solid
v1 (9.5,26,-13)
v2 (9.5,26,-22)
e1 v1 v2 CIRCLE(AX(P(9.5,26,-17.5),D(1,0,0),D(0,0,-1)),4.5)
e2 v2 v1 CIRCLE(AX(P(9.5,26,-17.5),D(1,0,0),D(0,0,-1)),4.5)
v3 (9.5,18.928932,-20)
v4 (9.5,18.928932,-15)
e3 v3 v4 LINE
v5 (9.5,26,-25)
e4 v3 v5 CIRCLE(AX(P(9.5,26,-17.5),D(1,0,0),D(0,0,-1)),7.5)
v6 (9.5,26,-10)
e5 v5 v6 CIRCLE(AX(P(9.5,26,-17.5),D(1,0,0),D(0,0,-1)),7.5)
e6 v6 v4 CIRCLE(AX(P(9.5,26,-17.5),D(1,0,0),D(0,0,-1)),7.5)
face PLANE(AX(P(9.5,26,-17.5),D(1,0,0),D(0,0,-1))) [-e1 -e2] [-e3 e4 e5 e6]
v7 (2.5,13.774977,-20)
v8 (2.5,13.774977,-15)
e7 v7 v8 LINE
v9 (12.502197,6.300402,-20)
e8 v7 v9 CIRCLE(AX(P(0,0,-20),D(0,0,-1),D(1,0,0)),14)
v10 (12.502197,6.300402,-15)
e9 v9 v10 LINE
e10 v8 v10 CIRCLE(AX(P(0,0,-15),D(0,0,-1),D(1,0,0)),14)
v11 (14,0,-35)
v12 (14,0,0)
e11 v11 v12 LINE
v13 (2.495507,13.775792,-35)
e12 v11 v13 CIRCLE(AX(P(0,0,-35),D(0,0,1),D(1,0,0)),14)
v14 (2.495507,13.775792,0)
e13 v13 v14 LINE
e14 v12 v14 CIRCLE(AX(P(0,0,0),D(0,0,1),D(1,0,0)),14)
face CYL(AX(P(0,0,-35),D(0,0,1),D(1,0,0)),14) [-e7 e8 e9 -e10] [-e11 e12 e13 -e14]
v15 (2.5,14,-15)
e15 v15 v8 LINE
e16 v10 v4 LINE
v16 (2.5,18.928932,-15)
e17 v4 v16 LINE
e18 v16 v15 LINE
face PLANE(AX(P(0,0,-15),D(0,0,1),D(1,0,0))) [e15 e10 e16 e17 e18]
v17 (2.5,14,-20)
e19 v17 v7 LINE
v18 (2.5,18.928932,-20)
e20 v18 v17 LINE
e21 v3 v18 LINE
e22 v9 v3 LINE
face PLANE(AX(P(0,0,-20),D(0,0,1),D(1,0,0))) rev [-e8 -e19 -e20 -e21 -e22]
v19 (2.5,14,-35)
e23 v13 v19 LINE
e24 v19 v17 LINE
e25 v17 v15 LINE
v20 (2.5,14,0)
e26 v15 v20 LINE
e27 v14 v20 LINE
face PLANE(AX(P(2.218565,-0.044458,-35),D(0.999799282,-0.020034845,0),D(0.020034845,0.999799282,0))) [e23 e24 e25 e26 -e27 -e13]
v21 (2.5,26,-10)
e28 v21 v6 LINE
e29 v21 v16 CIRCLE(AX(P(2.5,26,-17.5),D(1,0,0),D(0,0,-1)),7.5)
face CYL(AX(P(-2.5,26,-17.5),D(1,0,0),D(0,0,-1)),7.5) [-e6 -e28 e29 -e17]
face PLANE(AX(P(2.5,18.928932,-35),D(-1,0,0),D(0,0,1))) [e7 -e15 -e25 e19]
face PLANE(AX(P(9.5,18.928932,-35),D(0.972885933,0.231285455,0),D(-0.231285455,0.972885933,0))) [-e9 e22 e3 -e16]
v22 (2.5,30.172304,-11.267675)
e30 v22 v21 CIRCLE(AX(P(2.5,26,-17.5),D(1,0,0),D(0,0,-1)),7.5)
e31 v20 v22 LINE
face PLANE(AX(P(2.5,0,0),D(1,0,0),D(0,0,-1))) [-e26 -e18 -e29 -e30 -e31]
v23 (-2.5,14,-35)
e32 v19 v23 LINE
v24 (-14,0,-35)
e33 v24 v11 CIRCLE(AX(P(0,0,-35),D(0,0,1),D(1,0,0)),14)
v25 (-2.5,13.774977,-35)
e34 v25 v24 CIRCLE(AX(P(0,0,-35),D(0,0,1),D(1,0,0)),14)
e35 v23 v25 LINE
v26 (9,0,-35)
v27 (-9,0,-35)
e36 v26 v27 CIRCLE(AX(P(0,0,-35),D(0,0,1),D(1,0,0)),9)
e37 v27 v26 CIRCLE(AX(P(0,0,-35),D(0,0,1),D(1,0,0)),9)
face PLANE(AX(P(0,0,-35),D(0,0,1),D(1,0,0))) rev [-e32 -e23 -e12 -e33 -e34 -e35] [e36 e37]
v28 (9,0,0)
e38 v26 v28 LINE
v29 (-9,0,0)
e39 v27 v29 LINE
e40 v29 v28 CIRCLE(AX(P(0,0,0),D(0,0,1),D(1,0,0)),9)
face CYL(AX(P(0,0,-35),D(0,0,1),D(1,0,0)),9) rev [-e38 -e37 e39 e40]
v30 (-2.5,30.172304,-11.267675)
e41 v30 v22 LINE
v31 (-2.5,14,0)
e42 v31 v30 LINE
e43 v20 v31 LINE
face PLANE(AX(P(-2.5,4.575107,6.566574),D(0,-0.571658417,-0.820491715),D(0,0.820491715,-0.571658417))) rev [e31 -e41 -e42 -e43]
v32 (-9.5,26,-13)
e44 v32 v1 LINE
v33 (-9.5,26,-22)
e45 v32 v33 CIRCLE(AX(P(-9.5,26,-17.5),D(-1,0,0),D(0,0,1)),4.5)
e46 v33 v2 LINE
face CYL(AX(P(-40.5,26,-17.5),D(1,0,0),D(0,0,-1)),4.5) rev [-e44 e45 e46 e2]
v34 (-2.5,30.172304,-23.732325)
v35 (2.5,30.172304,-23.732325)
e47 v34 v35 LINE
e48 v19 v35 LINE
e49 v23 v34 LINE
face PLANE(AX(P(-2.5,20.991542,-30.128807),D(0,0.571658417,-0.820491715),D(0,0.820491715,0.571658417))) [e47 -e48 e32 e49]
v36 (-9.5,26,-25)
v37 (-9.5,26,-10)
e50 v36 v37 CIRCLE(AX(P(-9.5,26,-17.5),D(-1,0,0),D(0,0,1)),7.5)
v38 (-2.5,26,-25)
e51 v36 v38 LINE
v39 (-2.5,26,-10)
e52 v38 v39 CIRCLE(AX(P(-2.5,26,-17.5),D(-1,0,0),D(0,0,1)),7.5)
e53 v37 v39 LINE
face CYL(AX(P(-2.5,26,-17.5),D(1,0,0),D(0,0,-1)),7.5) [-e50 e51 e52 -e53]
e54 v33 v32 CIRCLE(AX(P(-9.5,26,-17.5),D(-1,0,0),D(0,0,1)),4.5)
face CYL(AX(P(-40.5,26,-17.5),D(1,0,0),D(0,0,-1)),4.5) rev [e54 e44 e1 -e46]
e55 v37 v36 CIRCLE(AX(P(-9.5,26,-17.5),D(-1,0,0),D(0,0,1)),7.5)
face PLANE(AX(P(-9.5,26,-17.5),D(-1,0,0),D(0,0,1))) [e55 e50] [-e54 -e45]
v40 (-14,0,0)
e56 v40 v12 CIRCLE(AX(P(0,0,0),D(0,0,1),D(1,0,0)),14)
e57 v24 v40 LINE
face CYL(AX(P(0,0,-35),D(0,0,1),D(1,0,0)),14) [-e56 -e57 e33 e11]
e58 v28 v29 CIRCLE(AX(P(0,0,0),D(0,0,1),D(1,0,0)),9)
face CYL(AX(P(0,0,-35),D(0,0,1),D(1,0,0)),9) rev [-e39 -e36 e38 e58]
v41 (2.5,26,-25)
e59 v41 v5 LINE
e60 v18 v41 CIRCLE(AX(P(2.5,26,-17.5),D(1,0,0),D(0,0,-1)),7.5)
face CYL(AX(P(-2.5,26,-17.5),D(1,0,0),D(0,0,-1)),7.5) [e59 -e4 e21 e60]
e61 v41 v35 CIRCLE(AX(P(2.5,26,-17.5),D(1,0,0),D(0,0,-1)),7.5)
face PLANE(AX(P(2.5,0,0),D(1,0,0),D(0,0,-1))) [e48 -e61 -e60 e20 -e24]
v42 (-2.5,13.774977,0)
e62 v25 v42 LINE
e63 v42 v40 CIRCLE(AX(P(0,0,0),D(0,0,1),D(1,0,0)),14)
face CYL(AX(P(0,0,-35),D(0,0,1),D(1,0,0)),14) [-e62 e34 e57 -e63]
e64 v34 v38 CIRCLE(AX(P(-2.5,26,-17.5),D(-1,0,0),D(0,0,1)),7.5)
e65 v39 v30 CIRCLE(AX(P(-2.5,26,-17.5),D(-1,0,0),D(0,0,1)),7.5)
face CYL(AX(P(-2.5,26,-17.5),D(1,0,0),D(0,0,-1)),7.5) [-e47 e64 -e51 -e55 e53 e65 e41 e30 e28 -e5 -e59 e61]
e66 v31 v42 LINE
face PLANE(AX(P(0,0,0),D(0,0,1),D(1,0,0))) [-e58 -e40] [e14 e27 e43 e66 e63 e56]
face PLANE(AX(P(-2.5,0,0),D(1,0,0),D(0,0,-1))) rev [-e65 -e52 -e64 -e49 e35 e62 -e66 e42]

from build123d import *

# Parameters (mm, degrees)
MAIN_CYLINDER_SKETCH_R = 14
MAIN_CYLINDER_28_DEPTH = 35
MAIN_BORE_SKETCH_R     = 9
MAIN_BORE_18_DEPTH     = 35
BASE_WEB_SKETCH_R      = 7.5
BASE_WEB_DEPTH         = 2.5
SECOND_WEB_DEPTH       = 2.5
SUPPORT_RIB_DEPTH      = 5
UPPER_BOSS_A_SKETCH_R  = 7.5
UPPER_BOSS_A_15_DEPTH  = 7
UPPER_BOSS_B_SKETCH_R  = 7.5
UPPER_BOSS_B_15_DEPTH  = 7
BOSS_ARM_DEPTH         = 7
SADDLE_FILL_DEPTH      = 35
TRIM_CUT_1_DEPTH       = 15
TRIM_CUT_2_DEPTH       = 51.430645445
TRIM_CUT_2_DEPTH_BACK  = 15
TRIM_CUT_3_DEPTH       = 15
UPPER_BORE_SKETCH_R    = 4.5
UPPER_BORE_9_DEPTH     = 50
CYLINDER_SKIN_28_DEPTH = 35


with BuildPart() as part:
    # Main Cylinder Sketch → Main Cylinder Ø28 (new body)
    with BuildSketch(Plane.XY):
        Circle(MAIN_CYLINDER_SKETCH_R)
    extrude(amount=-MAIN_CYLINDER_28_DEPTH)

    # Main Bore Sketch → Main Bore Ø18 (cut)
    with BuildSketch(Plane.XY):
        Circle(MAIN_BORE_SKETCH_R)
    extrude(amount=-MAIN_BORE_18_DEPTH, mode=Mode.SUBTRACT)



with BuildPart() as body_2:
    # Base Web Sketch → Base Web (new body)
    with BuildSketch(Plane(origin=(0, 0, 0), x_dir=(0, 0, -1), z_dir=(1, 0, 0))):
        with Locations((17.5, 26)):
            Circle(BASE_WEB_SKETCH_R)
        with BuildLine():
            Line((35, 14), (25, 26))
            ThreePointArc((25, 26), (17.5, 18.5), (10, 26))
            Line((10, 26), (0, 14))
            Line((0, 14), (35, 14))
        make_face()
    extrude(amount=-BASE_WEB_DEPTH)

    # Second Web Sketch → Second Web (add)
    with BuildSketch(Plane(origin=(0, 0, 0), x_dir=(0, 0, -1), z_dir=(1, 0, 0))):
        with BuildLine():
            ThreePointArc((25, 26), (17.5, 33.5), (10, 26))
            ThreePointArc((10, 26), (17.5, 18.5), (25, 26))
        make_face()
        with BuildLine():
            Line((10, 26), (0, 14))
            Line((0, 14), (35, 14))
            Line((35, 14), (25, 26))
            ThreePointArc((25, 26), (17.5, 18.5), (10, 26))
        make_face()
    extrude(amount=SECOND_WEB_DEPTH)

    # Support Rib Sketch → Support Rib (add)
    with BuildSketch(Plane(origin=(2.5, 0, 0), x_dir=(0, 0, -1), z_dir=(1, 0, 0))):
        with BuildLine():
            Line((11.267674623, 30.172303968), (0, 14))
            Line((0, 14), (10, 26))
            ThreePointArc((10, 26), (10.323913311, 28.180316454), (11.267674623, 30.172303968))
        make_face()
        with BuildLine():
            Line((25, 26), (35, 14))
            Line((35, 14), (23.732325377, 30.172303968))
            ThreePointArc((23.732325377, 30.172303968), (24.676086689, 28.180316454), (25, 26))
        make_face()
    extrude(amount=-SUPPORT_RIB_DEPTH)

    # Upper Boss A Sketch → Upper Boss A Ø15 (add)
    with BuildSketch(Plane(origin=(2.5, 0, 0), x_dir=(0, 0, -1), z_dir=(1, 0, 0))):
        with Locations((17.5, 26)):
            Circle(UPPER_BOSS_A_SKETCH_R)
    extrude(amount=UPPER_BOSS_A_15_DEPTH)

    # Upper Boss B Sketch → Upper Boss B Ø15 (add)
    with BuildSketch(Plane.ZY.offset(2.5)):
        with Locations(Location((-17.5, 26, 0), (0, 0, 180))):
            Circle(UPPER_BOSS_B_SKETCH_R)
    extrude(amount=UPPER_BOSS_B_15_DEPTH)

    # Upper Bore Sketch → Upper Bore Ø9 (cut)
    with BuildSketch(Plane(origin=(9.5, 0, 0), x_dir=(0, 0, -1), z_dir=(1, 0, 0))):
        with Locations((17.5, 26)):
            Circle(UPPER_BORE_SKETCH_R)
    extrude(amount=-UPPER_BORE_9_DEPTH, mode=Mode.SUBTRACT)


with BuildPart() as body_3:
    # Boss Arm Sketch → Boss Arm (new body)
    with BuildSketch(Plane(origin=(9.5, 0, 0), x_dir=(0, 0, -1), z_dir=(1, 0, 0))):
        with BuildLine():
            Line((15, 18.5), (15, 18.928932188))
            ThreePointArc((15, 18.928932188), (17.5, 18.5), (20, 18.928932188))
            Line((20, 18.928932188), (20, 0))
            Line((20, 0), (15, 0))
            Line((15, 0), (15, 18.5))
        make_face()
    extrude(amount=-BOSS_ARM_DEPTH)

    # Trim Cut 3 Sketch → Trim Cut 3 (cut)
    with BuildSketch(Plane.XY.offset(-15)):
        with BuildLine():
            Line((2.5, 0), (9, 0))
            ThreePointArc((9, 0), (7.193747285, 5.408326913), (2.5, 8.645808233))
            Line((2.5, 8.645808233), (2.5, 0))
        make_face()
    extrude(amount=-TRIM_CUT_3_DEPTH, mode=Mode.SUBTRACT)


with BuildPart() as body_4:
    # Saddle Fill Sketch → Saddle Fill (new body)
    with BuildSketch(Plane.XY):
        with BuildLine():
            Line((9.5, 18.928932188), (12.50219707, 6.300402243))
            ThreePointArc((12.50219707, 6.300402243), (8.380560683, 11.214553163), (2.5, 13.774977314))
            Line((2.5, 13.774977314), (2.5, 18.928932188))
            Line((2.5, 18.928932188), (9.5, 18.928932188))
        make_face()
    extrude(amount=-SADDLE_FILL_DEPTH)

    # Trim Cut 1 Sketch → Trim Cut 1 (cut)
    with BuildSketch(Plane.XY):
        with BuildLine():
            Line((2.5, 18.928932188), (9.5, 18.928932188))
            Line((9.5, 18.928932188), (12.50219707, 6.300402243))
            ThreePointArc((12.50219707, 6.300402243), (8.380560683, 11.214553163), (2.5, 13.774977314))
            Line((2.5, 13.774977314), (2.5, 18.928932188))
        make_face()
    extrude(amount=-TRIM_CUT_1_DEPTH, mode=Mode.SUBTRACT)

    # Trim Cut 2 Sketch → Trim Cut 2 (cut, two sides: drawn at the far end of the back side and taken through both)
    with BuildSketch(Plane(origin=(0, 0, -35), x_dir=(-1, 0, 0), z_dir=(0, 0, -1)).offset(-TRIM_CUT_2_DEPTH_BACK)):
        with BuildLine():
            Line((-2.5, 18.928932188), (-9.5, 18.928932188))
            Line((-9.5, 18.928932188), (-12.50219707, 6.300402243))
            ThreePointArc((-12.50219707, 6.300402243), (-8.380560683, 11.214553163), (-2.5, 13.774977314))
            Line((-2.5, 13.774977314), (-2.5, 18.928932188))
        make_face()
    extrude(amount=TRIM_CUT_2_DEPTH + TRIM_CUT_2_DEPTH_BACK, mode=Mode.SUBTRACT)


with BuildPart() as part_1:
    add(part.part)

    add(body_2.part)  # Cylinder Skin Ø28 merges body 2

    add(body_3.part)  # Cylinder Skin Ø28 merges body 3

    add(body_4.part)  # Cylinder Skin Ø28 merges body 4
    # Cylinder Skin Sketch → Cylinder Skin Ø28 (add)
    with BuildSketch(Plane.XY):
        with BuildLine():
            Line((2.5, 14), (1.6e-08, 14))
            ThreePointArc((1.6e-08, 14), (1.252779423, 13.94383533), (2.495507125, 13.775791962))
            Line((2.495507125, 13.775791962), (2.5, 14))
        make_face()
        with BuildLine():
            Line((1.6e-08, 14), (-2.5, 14))
            Line((-2.5, 14), (-2.5, 13.774977314))
            ThreePointArc((-2.5, 13.774977314), (-1.255053299, 13.943630848), (1.6e-08, 14))
        make_face()
    extrude(amount=-CYLINDER_SKIN_28_DEPTH)


solid = part_1.part
